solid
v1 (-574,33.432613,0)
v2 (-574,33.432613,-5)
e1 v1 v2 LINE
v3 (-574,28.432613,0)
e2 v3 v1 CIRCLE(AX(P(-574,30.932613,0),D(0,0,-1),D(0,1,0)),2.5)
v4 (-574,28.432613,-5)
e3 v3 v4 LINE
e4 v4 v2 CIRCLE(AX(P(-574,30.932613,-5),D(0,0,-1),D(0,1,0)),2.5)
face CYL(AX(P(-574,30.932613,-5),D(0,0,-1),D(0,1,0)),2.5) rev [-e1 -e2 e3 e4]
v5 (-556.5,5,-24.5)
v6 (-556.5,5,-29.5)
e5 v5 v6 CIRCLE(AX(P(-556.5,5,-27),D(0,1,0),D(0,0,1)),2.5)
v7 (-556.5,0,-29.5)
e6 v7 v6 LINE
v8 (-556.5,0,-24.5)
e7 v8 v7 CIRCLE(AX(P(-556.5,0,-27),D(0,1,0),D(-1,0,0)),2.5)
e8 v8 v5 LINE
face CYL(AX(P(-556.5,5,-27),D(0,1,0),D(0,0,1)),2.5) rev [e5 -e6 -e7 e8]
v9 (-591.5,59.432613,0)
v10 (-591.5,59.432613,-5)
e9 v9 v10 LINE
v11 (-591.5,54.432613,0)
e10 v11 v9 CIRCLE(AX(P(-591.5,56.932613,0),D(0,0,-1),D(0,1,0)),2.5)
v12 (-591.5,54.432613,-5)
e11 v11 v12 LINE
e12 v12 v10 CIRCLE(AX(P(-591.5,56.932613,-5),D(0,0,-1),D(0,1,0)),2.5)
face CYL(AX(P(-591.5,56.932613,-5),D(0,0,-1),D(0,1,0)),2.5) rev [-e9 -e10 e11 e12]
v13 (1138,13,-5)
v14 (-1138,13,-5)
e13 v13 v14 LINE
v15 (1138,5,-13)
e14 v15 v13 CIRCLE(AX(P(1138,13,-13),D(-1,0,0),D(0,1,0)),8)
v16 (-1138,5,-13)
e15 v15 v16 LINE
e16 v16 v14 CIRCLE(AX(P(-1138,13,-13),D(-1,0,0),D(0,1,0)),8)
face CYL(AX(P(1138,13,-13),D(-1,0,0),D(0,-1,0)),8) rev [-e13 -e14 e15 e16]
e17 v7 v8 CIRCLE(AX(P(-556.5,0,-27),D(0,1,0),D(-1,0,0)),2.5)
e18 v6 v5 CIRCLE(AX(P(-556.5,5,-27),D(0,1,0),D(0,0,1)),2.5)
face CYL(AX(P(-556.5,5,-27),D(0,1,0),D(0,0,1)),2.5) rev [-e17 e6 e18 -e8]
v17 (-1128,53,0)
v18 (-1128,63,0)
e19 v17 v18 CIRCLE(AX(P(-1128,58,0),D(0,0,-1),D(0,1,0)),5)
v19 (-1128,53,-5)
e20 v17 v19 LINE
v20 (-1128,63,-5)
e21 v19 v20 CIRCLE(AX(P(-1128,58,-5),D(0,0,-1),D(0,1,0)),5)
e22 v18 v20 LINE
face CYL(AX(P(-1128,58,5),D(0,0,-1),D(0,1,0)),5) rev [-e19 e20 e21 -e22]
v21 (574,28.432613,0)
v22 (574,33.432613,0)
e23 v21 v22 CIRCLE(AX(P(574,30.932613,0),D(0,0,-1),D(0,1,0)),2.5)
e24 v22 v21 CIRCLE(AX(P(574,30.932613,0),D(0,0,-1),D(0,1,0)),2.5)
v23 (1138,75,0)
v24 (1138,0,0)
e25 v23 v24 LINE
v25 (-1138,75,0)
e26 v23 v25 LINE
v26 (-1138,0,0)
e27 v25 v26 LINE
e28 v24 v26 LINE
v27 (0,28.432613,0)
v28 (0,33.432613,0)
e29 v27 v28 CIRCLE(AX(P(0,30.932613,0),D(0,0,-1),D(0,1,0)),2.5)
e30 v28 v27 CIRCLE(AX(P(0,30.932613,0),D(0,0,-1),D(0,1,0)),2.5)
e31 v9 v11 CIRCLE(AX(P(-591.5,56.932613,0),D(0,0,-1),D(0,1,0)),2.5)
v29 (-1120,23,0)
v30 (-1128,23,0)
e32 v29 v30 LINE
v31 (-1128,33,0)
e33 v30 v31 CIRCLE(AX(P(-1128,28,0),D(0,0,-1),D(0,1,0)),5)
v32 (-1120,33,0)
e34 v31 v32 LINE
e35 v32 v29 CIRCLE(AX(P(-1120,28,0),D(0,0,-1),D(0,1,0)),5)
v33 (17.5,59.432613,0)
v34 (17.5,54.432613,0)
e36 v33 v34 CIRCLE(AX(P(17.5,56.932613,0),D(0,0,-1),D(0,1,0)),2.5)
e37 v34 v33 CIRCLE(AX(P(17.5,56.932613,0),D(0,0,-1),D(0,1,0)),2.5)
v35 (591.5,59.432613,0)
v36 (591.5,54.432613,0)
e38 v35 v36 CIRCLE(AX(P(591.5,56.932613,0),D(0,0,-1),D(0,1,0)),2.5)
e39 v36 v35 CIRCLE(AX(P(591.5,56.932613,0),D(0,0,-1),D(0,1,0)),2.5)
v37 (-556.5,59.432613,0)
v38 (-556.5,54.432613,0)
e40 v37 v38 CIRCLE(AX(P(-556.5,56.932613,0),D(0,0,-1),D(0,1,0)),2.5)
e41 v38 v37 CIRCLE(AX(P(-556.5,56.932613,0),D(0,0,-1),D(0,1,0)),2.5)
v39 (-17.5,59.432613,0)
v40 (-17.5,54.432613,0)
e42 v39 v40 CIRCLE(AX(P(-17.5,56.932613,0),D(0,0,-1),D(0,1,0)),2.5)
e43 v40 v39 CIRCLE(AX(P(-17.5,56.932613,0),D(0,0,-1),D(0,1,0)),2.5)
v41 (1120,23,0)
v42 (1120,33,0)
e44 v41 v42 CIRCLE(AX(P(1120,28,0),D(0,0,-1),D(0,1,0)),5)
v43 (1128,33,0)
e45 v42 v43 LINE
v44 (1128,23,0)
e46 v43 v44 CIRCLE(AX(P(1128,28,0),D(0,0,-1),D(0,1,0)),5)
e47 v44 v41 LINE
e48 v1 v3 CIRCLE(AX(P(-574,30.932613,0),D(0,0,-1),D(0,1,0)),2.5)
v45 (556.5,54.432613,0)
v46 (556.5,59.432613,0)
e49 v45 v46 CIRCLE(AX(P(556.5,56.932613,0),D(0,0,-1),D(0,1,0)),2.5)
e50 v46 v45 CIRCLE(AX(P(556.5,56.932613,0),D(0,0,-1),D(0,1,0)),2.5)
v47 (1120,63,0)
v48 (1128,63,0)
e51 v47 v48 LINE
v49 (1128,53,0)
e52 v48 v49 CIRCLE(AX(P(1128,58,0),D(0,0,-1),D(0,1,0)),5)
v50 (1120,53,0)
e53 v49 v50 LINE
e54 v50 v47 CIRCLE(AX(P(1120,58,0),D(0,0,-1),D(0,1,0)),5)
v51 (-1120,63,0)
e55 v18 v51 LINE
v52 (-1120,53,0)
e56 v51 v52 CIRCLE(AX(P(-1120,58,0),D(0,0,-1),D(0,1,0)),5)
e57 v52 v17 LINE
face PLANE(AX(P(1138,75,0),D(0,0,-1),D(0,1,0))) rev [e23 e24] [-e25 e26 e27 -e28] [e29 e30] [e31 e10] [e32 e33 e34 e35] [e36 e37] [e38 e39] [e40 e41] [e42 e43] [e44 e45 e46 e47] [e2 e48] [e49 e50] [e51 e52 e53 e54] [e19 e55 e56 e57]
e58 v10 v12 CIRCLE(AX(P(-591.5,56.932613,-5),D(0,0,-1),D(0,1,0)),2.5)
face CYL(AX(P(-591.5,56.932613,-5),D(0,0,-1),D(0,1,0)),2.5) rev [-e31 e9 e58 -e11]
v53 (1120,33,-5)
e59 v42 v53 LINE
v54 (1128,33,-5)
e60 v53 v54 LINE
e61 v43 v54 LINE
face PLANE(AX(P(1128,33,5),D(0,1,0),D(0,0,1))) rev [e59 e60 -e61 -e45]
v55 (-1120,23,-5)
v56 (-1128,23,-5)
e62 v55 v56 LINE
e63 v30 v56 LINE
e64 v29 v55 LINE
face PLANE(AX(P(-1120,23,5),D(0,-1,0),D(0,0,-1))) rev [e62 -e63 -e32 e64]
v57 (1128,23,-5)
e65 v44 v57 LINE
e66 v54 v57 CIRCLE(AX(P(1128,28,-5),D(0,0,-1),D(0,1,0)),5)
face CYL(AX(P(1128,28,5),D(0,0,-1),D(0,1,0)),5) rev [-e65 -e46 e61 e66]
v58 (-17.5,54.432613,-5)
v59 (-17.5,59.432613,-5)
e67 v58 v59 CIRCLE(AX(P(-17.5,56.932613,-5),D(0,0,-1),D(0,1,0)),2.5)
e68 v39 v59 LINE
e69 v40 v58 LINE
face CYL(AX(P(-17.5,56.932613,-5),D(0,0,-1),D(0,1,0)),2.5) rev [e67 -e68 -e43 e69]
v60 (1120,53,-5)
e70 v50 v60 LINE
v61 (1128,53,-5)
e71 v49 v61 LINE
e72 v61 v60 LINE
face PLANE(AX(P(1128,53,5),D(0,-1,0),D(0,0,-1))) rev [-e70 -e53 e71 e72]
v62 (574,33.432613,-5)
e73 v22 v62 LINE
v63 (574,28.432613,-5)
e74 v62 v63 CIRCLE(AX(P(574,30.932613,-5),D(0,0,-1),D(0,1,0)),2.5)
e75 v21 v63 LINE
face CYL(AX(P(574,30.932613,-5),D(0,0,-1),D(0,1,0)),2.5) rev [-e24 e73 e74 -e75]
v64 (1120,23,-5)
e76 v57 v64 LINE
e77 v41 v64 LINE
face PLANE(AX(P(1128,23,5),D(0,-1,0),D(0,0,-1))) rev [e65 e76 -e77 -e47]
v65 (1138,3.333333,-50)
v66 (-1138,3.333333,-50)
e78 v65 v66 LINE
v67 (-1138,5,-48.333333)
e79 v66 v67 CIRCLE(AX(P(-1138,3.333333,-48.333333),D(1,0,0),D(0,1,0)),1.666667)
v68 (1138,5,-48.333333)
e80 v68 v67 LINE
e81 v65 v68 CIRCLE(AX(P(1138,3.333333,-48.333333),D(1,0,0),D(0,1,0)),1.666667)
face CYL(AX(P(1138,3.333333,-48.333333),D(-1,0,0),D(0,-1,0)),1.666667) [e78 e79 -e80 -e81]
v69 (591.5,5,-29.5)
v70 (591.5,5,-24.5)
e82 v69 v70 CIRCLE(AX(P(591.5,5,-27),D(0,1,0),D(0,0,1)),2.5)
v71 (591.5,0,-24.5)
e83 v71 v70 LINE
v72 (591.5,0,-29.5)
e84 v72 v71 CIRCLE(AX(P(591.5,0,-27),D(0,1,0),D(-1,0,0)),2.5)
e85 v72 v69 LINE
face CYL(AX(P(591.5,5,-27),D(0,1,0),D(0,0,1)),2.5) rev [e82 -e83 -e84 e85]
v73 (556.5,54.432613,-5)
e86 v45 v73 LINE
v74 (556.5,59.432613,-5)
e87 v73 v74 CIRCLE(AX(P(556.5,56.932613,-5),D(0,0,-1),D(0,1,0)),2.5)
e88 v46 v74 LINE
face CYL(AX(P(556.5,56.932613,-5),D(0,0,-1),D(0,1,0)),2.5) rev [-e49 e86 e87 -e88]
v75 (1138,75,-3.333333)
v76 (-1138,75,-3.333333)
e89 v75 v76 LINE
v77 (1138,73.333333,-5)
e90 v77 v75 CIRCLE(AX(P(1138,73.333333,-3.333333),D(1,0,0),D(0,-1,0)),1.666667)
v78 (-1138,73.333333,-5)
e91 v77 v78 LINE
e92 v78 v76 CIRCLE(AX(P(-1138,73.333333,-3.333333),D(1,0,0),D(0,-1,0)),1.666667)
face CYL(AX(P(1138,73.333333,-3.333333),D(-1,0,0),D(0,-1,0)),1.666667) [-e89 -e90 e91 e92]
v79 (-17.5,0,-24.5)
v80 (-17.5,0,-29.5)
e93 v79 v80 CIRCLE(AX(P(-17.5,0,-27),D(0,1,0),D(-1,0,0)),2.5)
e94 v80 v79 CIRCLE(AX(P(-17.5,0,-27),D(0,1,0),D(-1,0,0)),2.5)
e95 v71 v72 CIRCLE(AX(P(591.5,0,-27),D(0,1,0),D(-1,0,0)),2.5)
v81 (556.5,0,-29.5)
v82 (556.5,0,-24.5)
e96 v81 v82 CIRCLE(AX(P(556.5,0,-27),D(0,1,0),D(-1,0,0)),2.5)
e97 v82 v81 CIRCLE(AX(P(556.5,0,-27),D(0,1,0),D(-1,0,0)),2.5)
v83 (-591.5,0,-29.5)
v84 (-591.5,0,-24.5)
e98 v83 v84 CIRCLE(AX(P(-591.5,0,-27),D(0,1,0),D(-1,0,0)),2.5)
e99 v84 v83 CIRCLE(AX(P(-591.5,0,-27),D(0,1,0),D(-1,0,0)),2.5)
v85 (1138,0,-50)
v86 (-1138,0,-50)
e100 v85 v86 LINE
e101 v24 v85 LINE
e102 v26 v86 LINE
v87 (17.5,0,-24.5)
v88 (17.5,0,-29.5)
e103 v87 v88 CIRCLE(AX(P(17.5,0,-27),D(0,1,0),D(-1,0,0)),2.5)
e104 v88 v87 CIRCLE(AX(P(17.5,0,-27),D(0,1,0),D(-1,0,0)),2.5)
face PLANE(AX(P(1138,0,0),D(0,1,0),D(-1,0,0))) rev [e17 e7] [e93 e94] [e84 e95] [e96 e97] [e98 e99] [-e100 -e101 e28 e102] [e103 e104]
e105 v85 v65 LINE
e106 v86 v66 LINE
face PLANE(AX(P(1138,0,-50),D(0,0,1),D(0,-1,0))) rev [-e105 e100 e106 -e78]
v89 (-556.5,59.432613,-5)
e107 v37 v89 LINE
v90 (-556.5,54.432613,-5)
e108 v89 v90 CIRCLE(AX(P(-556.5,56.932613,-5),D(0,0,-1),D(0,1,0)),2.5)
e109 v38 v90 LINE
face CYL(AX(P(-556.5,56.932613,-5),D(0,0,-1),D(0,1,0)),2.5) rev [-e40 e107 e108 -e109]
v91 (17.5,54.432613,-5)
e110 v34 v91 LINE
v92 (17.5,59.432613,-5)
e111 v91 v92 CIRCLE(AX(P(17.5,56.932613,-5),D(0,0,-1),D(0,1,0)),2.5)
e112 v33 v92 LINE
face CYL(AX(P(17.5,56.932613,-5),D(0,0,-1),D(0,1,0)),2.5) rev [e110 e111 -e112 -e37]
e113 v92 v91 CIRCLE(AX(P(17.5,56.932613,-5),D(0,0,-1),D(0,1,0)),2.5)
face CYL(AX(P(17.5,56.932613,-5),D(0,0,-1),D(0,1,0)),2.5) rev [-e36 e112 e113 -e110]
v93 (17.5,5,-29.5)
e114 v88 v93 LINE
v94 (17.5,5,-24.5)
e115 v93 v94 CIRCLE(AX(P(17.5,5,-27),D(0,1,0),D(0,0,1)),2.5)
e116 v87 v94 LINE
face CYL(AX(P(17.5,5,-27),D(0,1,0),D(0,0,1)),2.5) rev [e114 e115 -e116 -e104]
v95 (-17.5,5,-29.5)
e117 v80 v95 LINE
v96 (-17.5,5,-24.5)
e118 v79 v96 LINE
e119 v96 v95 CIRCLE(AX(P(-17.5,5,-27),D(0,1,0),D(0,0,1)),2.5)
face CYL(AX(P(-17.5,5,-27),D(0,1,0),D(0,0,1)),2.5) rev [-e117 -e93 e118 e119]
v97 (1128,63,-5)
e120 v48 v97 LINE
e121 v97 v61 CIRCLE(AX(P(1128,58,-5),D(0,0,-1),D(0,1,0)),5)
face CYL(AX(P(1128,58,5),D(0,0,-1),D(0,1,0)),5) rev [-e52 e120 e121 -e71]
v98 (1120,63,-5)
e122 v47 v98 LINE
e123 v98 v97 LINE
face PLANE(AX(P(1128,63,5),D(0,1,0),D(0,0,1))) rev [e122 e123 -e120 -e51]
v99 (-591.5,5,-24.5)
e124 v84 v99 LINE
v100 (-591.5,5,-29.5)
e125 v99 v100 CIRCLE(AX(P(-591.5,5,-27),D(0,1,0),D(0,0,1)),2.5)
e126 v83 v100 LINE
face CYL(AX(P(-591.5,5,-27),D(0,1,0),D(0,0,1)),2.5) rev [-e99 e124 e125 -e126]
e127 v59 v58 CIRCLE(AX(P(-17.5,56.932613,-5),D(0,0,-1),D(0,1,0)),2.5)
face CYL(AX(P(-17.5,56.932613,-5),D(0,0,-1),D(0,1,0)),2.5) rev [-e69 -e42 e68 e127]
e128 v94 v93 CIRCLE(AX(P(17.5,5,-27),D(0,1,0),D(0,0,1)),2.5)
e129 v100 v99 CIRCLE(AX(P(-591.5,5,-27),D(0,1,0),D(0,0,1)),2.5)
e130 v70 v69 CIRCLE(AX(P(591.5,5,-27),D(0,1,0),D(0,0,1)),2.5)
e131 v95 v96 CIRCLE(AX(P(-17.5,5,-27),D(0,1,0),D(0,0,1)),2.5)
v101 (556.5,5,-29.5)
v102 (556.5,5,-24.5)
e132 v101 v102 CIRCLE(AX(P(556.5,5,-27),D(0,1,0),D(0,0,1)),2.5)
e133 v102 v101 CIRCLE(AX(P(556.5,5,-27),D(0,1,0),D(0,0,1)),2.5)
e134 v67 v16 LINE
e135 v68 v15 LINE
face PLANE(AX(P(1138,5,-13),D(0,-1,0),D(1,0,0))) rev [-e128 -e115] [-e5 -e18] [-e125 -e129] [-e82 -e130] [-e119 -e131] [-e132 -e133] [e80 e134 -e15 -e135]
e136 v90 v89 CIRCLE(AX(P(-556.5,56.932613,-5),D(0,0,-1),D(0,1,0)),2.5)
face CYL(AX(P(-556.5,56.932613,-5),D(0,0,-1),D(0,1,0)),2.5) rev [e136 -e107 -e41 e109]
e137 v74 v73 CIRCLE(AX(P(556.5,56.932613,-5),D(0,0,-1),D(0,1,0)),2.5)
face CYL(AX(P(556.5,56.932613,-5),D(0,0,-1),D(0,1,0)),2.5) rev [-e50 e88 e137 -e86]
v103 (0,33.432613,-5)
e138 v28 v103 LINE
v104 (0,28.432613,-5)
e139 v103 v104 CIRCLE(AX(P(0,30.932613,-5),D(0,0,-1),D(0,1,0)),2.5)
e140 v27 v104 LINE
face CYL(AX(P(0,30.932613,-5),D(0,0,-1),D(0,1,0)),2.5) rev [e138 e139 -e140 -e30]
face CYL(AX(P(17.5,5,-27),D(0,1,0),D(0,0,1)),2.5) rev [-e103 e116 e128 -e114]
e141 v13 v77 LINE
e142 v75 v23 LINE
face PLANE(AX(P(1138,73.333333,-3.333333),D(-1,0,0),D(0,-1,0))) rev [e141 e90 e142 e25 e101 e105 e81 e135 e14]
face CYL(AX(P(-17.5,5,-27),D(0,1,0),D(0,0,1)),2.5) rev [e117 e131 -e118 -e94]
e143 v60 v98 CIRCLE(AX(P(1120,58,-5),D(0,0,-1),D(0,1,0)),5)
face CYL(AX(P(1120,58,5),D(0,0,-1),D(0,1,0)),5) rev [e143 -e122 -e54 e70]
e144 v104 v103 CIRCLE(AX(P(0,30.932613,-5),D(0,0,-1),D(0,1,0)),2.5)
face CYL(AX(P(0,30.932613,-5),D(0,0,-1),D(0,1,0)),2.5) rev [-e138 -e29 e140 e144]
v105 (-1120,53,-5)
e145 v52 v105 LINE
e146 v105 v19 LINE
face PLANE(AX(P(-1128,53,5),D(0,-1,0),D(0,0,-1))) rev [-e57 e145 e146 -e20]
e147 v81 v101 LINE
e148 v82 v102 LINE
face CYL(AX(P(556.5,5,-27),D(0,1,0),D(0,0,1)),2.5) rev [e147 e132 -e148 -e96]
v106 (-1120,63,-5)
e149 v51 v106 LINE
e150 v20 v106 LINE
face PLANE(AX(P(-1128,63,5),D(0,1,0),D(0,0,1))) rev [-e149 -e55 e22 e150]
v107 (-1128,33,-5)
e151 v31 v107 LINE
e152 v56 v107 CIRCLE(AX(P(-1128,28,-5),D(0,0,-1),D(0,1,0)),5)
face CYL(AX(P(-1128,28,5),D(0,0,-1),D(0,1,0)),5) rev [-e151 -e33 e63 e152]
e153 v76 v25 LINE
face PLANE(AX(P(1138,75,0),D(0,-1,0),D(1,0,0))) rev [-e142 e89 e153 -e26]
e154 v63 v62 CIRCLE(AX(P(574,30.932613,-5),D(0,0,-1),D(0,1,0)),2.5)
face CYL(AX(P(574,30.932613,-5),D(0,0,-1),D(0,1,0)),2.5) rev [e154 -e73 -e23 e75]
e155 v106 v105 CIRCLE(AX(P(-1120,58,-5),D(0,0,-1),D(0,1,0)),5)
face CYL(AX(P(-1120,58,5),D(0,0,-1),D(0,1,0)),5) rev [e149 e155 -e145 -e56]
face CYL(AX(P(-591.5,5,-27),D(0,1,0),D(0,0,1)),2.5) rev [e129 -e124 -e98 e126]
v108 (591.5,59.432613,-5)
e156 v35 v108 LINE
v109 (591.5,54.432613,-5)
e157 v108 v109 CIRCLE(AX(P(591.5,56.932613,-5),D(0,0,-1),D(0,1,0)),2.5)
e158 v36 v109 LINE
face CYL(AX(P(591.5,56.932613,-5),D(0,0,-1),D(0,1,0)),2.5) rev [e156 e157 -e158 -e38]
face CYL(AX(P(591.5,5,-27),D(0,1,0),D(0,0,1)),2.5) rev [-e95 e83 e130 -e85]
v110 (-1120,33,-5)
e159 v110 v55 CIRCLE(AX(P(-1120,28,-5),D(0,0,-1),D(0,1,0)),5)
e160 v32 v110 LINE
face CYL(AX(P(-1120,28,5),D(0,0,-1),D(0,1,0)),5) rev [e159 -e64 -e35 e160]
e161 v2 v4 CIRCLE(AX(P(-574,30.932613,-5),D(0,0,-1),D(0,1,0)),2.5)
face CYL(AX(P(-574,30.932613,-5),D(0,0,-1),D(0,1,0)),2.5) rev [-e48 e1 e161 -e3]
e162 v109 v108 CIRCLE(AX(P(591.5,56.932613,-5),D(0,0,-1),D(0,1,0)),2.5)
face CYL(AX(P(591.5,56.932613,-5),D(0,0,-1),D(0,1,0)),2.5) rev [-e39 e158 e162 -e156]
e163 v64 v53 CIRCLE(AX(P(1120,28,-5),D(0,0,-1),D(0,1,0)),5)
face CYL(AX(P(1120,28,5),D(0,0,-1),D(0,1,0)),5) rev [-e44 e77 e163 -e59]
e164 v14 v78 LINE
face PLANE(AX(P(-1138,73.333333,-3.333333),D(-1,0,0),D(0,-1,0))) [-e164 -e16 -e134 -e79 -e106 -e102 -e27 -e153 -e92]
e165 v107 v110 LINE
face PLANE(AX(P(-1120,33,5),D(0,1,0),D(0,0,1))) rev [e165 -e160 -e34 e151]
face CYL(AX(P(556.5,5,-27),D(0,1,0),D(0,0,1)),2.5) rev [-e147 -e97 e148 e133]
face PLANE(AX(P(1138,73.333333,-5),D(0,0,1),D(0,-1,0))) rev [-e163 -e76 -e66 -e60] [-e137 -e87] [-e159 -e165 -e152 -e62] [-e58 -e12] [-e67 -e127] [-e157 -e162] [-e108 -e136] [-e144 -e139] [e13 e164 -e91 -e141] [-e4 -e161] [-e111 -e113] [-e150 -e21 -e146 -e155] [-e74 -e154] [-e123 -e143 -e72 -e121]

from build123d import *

# Parameters (mm, degrees)
UNEQUAL_ANGLE_7_5_5_5_1_DEPTH = 2276
M6_TAPPED_HOLE2_D             = 5
M6_TAPPED_HOLE2_DEPTH         = 15
M6_TAPPED_HOLE2_TIP           = 1.502151548
M6_TAPPED_HOLE1_D             = 5
M6_TAPPED_HOLE1_DEPTH         = 15
M6_TAPPED_HOLE1_TIP           = 1.502151548
CUT_EXTRUDE1_DEPTH            = 10


with BuildPart() as part:
    # Sketch19 → Unequal angle 7.5-5-5(1) (new body)
    with BuildSketch(Plane.YZ.offset(-1138)):
        with BuildLine():
            Line((75, 0), (0, 0))
            Line((0, 0), (0, -50))
            Line((0, -50), (3.333333333, -50))
            ThreePointArc((3.333333333, -50), (4.511844635, -49.511844635), (5, -48.333333333))
            Line((5, -48.333333333), (5, -13))
            ThreePointArc((5, -13), (7.343145751, -7.343145751), (13, -5))
            Line((13, -5), (73.333333333, -5))
            ThreePointArc((73.333333333, -5), (74.511844635, -4.511844635), (75, -3.333333333))
            Line((75, -3.333333333), (75, 0))
        make_face()
    extrude(amount=UNEQUAL_ANGLE_7_5_5_5_1_DEPTH)

    # M6 Tapped Hole2
    with Locations(Plane(origin=(0, 5, 0), x_dir=(1, 0, 0), z_dir=(0, 1, 0))):
        with Locations((-591.5, 27), (-556.5, 27), (17.5, 27), (-17.5, 27), (591.5, 27), (556.5, 27)):
            Hole(M6_TAPPED_HOLE2_D / 2, depth=M6_TAPPED_HOLE2_DEPTH)
            with Locations((0, 0, -(M6_TAPPED_HOLE2_DEPTH + M6_TAPPED_HOLE2_TIP / 2))):  # 118° drill point
                Cone(0, M6_TAPPED_HOLE2_D / 2, M6_TAPPED_HOLE2_TIP, mode=Mode.SUBTRACT)

    # M6 Tapped Hole1
    with Locations(Plane(origin=(0, 0, -5), x_dir=(-1, 0, 0), z_dir=(0, 0, -1))):
        with Locations((17.5, 56.932613047), (-591.5, 56.932613047), (-556.5, 56.932613047), (-574, 30.932613047), (556.5, 56.932613047), (591.5, 56.932613047), (574, 30.932613047), (-17.5, 56.932613047), (0, 30.932613047)):
            Hole(M6_TAPPED_HOLE1_D / 2, depth=M6_TAPPED_HOLE1_DEPTH)
            with Locations((0, 0, -(M6_TAPPED_HOLE1_DEPTH + M6_TAPPED_HOLE1_TIP / 2))):  # 118° drill point
                Cone(0, M6_TAPPED_HOLE1_D / 2, M6_TAPPED_HOLE1_TIP, mode=Mode.SUBTRACT)

    # Sketch12 → Cut-Extrude1 (cut)
    with BuildSketch(Plane(origin=(0, 0, -5), x_dir=(-1, 0, 0), z_dir=(0, 0, -1))):
        with BuildLine():
            Line((1128, 53), (1120, 53))
            ThreePointArc((1120, 53), (1115, 58), (1120, 63))
            Line((1120, 63), (1128, 63))
            ThreePointArc((1128, 63), (1133, 58), (1128, 53))
        make_face()
        with BuildLine():
            Line((1120, 33), (1128, 33))
            ThreePointArc((1128, 33), (1133, 28), (1128, 23))
            Line((1128, 23), (1120, 23))
            ThreePointArc((1120, 23), (1115, 28), (1120, 33))
        make_face()
        with BuildLine():
            Line((-1128, 63), (-1120, 63))
            ThreePointArc((-1120, 63), (-1115, 58), (-1120, 53))
            Line((-1120, 53), (-1128, 53))
            ThreePointArc((-1128, 53), (-1133, 58), (-1128, 63))
        make_face()
        with BuildLine():
            Line((-1128, 33), (-1120, 33))
            ThreePointArc((-1120, 33), (-1115, 28), (-1120, 23))
            Line((-1120, 23), (-1128, 23))
            ThreePointArc((-1128, 23), (-1133, 28), (-1128, 33))
        make_face()
    extrude(amount=-CUT_EXTRUDE1_DEPTH, mode=Mode.SUBTRACT)


solid = part.part
